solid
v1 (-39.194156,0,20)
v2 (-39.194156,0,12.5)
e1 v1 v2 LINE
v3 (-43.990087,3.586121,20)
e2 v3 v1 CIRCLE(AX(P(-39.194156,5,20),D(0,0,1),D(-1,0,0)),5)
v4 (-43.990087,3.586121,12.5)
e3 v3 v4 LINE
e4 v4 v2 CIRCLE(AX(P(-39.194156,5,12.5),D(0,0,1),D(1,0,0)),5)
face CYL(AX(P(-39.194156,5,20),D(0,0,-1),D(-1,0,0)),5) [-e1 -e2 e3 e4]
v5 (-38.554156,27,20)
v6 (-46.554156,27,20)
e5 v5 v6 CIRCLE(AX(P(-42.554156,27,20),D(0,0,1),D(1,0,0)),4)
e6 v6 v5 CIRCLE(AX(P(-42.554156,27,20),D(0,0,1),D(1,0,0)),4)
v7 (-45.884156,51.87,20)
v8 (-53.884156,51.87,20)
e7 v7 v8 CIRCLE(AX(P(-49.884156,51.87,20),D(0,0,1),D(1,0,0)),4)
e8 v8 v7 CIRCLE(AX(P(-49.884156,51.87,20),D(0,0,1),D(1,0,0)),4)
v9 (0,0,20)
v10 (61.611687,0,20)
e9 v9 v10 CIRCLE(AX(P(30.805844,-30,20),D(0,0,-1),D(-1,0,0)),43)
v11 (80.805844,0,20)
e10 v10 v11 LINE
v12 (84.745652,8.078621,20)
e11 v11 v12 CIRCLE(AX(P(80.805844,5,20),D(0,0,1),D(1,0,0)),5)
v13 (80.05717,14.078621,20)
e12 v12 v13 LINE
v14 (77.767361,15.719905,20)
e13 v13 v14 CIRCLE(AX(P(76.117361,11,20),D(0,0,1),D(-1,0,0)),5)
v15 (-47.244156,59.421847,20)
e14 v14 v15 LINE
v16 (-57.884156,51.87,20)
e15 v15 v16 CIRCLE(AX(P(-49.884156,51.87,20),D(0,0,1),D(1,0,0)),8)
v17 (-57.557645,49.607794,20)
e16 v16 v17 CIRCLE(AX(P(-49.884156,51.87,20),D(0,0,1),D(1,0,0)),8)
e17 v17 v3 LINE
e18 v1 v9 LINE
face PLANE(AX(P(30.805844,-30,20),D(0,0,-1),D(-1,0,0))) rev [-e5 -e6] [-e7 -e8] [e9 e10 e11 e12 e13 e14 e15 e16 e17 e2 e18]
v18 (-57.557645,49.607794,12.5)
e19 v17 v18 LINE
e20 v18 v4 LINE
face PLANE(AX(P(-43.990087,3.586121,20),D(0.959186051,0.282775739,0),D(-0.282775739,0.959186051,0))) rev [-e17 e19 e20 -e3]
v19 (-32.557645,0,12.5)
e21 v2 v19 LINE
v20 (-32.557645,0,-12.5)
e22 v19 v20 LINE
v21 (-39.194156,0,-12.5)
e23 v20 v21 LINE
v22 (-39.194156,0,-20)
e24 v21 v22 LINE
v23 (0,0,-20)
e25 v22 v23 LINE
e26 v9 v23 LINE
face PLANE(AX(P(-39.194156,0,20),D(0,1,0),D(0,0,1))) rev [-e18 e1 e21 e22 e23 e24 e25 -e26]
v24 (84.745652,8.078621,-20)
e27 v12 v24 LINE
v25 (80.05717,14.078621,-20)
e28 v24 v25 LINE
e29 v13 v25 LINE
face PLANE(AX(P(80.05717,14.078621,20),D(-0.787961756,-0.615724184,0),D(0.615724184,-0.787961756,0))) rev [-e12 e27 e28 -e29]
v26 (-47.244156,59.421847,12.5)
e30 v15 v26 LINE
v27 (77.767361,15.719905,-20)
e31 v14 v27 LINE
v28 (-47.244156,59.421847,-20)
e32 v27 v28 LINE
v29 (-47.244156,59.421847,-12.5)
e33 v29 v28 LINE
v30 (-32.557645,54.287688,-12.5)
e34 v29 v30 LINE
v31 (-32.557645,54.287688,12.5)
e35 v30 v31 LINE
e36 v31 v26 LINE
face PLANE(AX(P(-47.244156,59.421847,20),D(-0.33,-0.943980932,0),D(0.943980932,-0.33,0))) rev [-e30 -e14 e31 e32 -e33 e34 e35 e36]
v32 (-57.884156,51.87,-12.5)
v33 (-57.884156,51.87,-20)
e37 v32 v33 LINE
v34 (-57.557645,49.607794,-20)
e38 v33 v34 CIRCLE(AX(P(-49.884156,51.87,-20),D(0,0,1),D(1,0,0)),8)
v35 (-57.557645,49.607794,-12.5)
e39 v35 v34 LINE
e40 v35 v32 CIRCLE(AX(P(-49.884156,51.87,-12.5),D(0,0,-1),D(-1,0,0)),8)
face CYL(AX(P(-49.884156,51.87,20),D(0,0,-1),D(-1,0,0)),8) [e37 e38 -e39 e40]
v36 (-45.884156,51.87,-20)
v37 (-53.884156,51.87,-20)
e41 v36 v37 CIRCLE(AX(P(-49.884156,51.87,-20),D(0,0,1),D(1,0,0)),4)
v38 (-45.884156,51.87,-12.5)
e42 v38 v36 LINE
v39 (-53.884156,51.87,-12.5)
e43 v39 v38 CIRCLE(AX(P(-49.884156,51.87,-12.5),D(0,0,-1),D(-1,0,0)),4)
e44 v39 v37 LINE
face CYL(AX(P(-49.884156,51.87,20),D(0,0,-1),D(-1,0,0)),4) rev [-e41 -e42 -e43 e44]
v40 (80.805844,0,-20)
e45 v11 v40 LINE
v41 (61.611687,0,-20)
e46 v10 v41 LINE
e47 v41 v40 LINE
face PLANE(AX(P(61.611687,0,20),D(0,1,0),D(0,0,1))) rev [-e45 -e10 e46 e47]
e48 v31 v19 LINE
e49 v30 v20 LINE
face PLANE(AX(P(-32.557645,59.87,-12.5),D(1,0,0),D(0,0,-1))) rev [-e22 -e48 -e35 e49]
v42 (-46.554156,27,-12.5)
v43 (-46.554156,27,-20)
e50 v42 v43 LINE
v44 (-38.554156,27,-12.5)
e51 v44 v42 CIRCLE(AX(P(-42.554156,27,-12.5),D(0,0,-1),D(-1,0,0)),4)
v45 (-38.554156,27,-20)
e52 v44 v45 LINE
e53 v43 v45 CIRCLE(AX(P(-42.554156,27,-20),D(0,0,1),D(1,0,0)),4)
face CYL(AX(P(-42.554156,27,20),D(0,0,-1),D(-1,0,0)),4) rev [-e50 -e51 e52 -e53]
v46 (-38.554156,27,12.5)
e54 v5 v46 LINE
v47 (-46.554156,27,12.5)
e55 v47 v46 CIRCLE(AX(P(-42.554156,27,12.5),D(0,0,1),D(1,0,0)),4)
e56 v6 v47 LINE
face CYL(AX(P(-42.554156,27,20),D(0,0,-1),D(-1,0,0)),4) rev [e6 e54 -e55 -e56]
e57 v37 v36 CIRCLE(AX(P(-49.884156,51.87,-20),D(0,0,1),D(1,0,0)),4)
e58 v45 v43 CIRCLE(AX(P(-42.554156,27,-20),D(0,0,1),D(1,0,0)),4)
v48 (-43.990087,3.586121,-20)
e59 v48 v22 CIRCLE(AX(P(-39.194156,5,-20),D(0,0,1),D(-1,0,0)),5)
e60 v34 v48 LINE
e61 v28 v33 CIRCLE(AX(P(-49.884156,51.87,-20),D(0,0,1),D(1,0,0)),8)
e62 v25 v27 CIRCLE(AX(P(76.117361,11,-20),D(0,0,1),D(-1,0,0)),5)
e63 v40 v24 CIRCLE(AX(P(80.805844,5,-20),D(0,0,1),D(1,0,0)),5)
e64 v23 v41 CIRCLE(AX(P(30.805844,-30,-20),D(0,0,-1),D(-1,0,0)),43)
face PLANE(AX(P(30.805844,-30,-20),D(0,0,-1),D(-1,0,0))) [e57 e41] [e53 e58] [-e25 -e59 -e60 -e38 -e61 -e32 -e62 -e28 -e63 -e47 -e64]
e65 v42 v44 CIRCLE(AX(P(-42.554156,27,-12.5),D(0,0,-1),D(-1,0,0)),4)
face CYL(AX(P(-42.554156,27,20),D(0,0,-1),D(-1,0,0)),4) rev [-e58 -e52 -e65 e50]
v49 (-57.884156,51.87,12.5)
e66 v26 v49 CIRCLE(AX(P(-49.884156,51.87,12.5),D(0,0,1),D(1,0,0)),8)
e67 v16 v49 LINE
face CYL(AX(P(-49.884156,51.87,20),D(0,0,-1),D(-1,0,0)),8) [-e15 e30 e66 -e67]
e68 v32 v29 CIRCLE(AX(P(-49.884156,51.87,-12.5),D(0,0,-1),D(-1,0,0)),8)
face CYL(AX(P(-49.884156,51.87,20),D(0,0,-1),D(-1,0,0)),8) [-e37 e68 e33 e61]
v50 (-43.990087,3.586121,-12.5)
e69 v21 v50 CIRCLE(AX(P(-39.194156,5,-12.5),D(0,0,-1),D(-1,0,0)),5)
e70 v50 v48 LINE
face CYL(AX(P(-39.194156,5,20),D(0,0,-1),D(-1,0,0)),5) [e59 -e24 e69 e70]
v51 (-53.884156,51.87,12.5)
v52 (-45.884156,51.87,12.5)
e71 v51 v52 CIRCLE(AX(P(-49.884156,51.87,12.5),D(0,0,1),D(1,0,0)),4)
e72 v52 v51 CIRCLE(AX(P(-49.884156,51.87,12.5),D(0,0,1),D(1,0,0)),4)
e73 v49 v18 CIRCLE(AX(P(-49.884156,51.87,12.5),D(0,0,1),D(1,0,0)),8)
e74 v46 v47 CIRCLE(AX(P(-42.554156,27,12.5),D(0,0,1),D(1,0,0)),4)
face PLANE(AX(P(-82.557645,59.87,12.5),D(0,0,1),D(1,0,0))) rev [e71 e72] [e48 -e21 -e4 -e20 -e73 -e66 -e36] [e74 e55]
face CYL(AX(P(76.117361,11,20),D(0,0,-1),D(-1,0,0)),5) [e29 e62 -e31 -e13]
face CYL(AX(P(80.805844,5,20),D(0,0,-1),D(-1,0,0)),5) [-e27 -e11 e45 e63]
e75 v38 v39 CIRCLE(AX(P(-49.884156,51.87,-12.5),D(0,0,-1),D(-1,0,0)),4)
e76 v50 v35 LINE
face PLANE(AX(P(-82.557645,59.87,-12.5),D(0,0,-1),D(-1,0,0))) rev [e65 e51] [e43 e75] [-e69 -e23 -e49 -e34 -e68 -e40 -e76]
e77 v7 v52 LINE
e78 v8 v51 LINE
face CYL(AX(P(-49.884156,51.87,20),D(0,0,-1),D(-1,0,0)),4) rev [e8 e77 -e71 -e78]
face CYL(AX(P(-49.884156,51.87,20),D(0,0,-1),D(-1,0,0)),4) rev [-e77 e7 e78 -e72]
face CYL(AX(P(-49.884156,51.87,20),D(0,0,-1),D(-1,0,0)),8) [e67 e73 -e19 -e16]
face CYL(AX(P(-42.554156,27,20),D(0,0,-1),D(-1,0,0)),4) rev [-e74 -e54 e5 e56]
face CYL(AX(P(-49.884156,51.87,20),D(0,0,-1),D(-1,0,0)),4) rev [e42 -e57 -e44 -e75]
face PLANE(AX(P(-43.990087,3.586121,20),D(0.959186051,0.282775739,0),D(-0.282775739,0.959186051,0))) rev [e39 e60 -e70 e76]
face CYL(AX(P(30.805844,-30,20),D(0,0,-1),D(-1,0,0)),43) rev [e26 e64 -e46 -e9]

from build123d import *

# Parameters (mm, degrees)
JAW_PROFILE_SKETCH_R        = 4
JAW_PLATE_40MM_DEPTH        = 20
CLEVIS_SLOT_25MM_DEPTH      = 107.52257834
CLEVIS_SLOT_25MM_DEPTH_BACK = 107.52257834
CLEVIS_SLOT_SKETCH_W        = 50
CLEVIS_SLOT_SKETCH_H        = 25


with BuildPart() as part:
    # Jaw Profile Sketch → Jaw Plate 40mm (new, symmetric)
    with BuildSketch(Plane.XY):
        with BuildLine():
            Line((-39.194156399, 0), (0, 0))
            ThreePointArc((0, 0), (30.805843601, 13), (61.611687203, 0))
            Line((61.611687203, 0), (80.805843601, 0))
            ThreePointArc((80.805843601, 0), (85.299901044, 2.808323085), (84.745652382, 8.07862092))
            Line((84.745652382, 8.07862092), (80.057169629, 14.07862092))
            ThreePointArc((80.057169629, 14.07862092), (79.030253505, 15.063872091), (77.767360848, 15.71990466))
            Line((77.767360848, 15.71990466), (-47.244156399, 59.421847456))
            ThreePointArc((-47.244156399, 59.421847456), (-55.398946719, 57.665436802), (-57.55764481, 49.607794087))
            Line((-57.55764481, 49.607794087), (-43.990086656, 3.586121305))
            ThreePointArc((-43.990086656, 3.586121305), (-42.188368025, 0.995665256), (-39.194156399, 0))
        make_face()
        with Locations((-49.884156399, 51.87)):
            Circle(JAW_PROFILE_SKETCH_R, mode=Mode.SUBTRACT)
        with Locations((-42.554156399, 27)):
            Circle(JAW_PROFILE_SKETCH_R, mode=Mode.SUBTRACT)
    extrude(amount=JAW_PLATE_40MM_DEPTH, both=True)

    # Clevis Slot Sketch → Clevis Slot 25mm (cut, two sides: drawn at the far end of the back side and taken through both)
    with BuildSketch(Plane.XZ.offset(-CLEVIS_SLOT_25MM_DEPTH_BACK)):
        with Locations((-57.55764481, 0)):
            Rectangle(CLEVIS_SLOT_SKETCH_W, CLEVIS_SLOT_SKETCH_H)
    extrude(amount=CLEVIS_SLOT_25MM_DEPTH + CLEVIS_SLOT_25MM_DEPTH_BACK, mode=Mode.SUBTRACT)


solid = part.part
